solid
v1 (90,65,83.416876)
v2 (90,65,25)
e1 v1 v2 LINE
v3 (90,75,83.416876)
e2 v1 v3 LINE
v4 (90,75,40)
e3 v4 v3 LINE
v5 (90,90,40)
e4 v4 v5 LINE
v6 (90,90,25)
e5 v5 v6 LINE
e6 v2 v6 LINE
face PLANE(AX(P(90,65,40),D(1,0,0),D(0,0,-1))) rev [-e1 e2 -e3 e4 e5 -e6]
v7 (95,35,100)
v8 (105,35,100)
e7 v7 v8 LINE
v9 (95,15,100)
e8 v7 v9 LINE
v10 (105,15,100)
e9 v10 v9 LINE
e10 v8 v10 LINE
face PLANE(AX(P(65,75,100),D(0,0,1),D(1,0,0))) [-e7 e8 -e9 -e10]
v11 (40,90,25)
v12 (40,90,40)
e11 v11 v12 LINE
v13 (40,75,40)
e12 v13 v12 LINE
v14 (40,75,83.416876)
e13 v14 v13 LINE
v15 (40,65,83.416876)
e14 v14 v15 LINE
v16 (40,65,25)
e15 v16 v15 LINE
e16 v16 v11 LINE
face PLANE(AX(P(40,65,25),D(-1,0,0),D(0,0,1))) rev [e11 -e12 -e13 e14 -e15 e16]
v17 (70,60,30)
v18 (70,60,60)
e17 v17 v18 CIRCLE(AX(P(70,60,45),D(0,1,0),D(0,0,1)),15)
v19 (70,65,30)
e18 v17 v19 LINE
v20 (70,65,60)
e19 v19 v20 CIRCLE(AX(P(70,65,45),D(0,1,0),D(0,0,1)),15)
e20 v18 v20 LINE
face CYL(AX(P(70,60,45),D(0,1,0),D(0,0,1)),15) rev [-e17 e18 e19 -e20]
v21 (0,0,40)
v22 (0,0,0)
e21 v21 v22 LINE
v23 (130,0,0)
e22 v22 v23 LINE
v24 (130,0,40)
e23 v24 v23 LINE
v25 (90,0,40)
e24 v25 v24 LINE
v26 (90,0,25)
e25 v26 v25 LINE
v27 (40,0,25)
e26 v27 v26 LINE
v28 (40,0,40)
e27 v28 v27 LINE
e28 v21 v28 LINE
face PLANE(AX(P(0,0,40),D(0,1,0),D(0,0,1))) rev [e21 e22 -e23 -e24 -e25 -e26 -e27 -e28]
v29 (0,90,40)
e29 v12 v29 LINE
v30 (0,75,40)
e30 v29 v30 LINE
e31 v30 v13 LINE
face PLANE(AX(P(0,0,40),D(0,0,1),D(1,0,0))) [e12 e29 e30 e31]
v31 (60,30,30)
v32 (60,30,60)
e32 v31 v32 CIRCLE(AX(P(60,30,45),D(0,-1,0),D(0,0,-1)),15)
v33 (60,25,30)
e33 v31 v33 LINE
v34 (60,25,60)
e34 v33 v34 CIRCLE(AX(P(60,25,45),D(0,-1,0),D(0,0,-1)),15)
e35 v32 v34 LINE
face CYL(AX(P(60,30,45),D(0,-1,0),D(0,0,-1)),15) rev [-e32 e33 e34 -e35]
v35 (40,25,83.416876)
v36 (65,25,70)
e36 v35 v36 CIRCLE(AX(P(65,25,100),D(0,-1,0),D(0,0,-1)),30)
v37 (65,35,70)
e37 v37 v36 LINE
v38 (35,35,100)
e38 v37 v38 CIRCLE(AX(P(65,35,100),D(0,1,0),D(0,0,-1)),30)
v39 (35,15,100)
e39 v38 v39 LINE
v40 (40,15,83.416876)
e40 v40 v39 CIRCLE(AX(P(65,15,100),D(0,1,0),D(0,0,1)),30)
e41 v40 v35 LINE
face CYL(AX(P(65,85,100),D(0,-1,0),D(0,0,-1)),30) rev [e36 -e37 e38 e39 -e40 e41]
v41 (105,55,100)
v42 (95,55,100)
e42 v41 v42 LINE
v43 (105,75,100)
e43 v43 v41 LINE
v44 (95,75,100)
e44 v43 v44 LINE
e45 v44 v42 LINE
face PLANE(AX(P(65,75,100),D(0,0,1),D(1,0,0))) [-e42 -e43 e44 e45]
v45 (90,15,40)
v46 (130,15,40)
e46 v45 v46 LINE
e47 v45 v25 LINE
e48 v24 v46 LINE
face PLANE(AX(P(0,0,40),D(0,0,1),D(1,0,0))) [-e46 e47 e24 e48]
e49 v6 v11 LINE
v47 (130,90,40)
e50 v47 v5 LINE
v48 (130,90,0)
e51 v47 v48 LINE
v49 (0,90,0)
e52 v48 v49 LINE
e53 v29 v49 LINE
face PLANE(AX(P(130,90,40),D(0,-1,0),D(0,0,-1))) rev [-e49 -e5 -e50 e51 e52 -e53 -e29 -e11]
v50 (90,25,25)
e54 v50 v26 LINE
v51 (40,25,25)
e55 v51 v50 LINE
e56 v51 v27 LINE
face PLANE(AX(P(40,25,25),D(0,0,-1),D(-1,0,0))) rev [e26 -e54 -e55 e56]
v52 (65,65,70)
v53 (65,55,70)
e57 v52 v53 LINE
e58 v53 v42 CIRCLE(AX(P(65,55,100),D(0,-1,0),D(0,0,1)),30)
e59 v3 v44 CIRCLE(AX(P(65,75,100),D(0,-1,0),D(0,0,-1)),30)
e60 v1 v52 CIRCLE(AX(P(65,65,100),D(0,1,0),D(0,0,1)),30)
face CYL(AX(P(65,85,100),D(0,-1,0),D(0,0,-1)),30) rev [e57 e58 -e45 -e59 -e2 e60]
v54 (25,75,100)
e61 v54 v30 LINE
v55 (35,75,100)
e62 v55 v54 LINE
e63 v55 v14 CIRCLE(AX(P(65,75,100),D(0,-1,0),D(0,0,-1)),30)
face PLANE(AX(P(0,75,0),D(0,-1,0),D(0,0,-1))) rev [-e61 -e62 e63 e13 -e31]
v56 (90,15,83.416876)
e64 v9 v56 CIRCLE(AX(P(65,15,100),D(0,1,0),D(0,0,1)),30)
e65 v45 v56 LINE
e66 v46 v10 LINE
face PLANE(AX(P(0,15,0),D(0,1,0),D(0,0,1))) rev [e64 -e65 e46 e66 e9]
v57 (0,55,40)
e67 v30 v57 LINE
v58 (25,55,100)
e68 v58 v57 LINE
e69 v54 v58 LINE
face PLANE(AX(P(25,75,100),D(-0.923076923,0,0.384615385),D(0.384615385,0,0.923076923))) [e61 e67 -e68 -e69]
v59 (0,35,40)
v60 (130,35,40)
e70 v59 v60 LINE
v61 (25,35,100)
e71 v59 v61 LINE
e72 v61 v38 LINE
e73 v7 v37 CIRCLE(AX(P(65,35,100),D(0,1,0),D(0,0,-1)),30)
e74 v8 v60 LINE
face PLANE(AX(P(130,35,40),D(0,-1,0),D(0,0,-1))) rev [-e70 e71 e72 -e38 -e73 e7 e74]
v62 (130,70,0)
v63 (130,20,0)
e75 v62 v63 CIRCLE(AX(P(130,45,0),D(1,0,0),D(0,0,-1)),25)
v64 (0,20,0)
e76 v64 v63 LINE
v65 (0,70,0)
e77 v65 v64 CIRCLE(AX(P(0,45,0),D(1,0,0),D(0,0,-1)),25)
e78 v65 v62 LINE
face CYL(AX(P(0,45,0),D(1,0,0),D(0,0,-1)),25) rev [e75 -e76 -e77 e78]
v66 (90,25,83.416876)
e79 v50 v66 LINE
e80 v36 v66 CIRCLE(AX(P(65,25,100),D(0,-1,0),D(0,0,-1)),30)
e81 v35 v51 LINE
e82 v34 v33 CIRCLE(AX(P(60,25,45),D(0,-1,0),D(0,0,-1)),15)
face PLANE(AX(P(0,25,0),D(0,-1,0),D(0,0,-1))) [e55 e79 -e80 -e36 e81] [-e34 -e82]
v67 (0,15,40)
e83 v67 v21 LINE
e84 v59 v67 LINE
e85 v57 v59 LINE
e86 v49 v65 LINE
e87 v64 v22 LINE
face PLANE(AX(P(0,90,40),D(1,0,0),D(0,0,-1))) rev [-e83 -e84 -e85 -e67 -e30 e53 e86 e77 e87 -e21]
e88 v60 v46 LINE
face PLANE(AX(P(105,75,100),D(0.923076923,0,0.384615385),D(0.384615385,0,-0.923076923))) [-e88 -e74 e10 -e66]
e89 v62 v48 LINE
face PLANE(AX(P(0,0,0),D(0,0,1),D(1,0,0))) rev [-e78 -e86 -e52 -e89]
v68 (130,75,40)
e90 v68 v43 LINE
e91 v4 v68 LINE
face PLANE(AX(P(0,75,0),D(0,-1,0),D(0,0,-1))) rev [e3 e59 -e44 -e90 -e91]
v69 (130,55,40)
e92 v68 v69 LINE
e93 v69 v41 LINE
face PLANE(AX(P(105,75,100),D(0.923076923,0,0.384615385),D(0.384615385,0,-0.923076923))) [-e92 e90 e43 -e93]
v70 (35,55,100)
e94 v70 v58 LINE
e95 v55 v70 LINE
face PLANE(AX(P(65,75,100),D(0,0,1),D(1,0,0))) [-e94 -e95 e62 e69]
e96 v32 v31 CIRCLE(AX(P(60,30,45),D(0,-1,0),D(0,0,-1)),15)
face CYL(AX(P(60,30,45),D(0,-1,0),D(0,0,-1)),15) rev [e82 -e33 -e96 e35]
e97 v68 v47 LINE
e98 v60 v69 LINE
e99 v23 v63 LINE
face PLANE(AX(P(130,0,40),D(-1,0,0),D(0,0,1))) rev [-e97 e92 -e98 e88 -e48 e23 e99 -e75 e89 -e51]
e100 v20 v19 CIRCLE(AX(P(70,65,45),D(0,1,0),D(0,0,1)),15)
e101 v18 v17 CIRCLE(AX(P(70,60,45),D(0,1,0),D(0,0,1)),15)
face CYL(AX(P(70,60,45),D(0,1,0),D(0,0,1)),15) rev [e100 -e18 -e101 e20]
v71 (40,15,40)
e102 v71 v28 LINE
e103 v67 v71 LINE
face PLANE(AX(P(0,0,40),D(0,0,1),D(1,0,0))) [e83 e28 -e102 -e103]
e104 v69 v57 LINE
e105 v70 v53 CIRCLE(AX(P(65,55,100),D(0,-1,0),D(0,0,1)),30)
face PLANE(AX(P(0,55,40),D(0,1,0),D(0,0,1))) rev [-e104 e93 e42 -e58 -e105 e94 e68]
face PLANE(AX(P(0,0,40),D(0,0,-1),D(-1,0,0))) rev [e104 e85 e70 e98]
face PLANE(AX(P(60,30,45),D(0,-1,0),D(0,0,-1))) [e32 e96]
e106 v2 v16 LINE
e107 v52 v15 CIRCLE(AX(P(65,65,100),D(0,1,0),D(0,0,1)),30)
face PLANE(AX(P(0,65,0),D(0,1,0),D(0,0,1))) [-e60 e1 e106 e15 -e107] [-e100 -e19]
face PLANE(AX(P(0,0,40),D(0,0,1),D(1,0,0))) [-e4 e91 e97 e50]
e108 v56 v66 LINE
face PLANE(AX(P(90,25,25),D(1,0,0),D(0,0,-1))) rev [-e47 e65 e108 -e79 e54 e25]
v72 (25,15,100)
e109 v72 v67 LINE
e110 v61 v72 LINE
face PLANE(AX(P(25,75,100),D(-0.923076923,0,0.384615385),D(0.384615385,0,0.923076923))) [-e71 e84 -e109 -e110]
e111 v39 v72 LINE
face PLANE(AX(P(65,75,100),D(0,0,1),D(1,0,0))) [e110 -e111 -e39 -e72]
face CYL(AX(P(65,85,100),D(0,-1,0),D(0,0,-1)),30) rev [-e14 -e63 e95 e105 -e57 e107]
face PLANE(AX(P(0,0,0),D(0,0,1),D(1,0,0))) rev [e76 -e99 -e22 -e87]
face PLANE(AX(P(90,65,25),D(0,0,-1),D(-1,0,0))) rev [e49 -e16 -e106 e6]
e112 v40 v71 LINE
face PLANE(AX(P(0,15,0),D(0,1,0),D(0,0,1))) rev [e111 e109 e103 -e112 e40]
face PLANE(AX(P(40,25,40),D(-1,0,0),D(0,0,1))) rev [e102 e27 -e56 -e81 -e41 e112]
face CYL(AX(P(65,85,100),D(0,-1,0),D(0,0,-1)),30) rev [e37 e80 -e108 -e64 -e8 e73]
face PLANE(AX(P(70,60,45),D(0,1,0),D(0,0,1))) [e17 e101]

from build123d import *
from build123d.topology import SkipClean

# Parameters (mm, degrees)
BASE_BLOCK_SKETCH_W             = 130
BASE_BLOCK_SKETCH_H             = 90
BASE_BLOCK_40_DEPTH             = 40
SIDE_POCKET_A_25_DEPTH          = 25
SIDE_POCKET_B_25_DEPTH          = 25
UPPER_BOSS_50_DEPTH             = 50
WEB_BOSS_10_DEPTH               = 10
WEB_NOTCH_A_10_DEPTH            = 10
WEB_NOTCH_B_10_DEPTH            = 10
SLOT_CUT_A_60_DEPTH             = 60
SLOT_START                      = -60
SLOT_CUT_B_60_DEPTH             = 60
SLOT_CUT_C_60_DEPTH             = 60
SPOT_FACE_A_SKETCH_R            = 15
SPOT_FACE_A_30X5_DEPTH          = 5
SPOT_FACE_B_SKETCH_R            = 15
SPOT_FACE_B_30X5_DEPTH          = 5
BEARING_CRADLE_50_THROUGH_DEPTH = 130


with BuildPart() as part:
    # Base Block Sketch → Base Block 40 (new body)
    with BuildSketch(Plane.XY):
        with Locations((65, 45)):
            Rectangle(BASE_BLOCK_SKETCH_W, BASE_BLOCK_SKETCH_H)
    extrude(amount=BASE_BLOCK_40_DEPTH)

    # Side Pocket A Sketch → Side Pocket A 25 (cut)
    with BuildSketch(Plane.XZ):
        Polygon((65, 40), (40, 40), (40, 25), (90, 25), (90, 40), align=None)
    extrude(amount=-SIDE_POCKET_A_25_DEPTH, mode=Mode.SUBTRACT)

    # Side Pocket B Sketch → Side Pocket B 25 (cut)
    with BuildSketch(Plane(origin=(0, 90, 0), x_dir=(1, 0, 0), z_dir=(0, 1, 0))):
        Polygon((65, -40), (90, -40), (90, -25), (40, -25), (40, -40), align=None)
    extrude(amount=-SIDE_POCKET_B_25_DEPTH, mode=Mode.SUBTRACT)

    # Upper Boss Sketch → Upper Boss 50 (add)
    with BuildSketch(Plane.XZ.offset(-25)):
        Polygon((65, 100), (105, 100), (130, 40), (0, 40), (25, 100), align=None)
    extrude(amount=-UPPER_BOSS_50_DEPTH)

    # Web Boss Sketch → Web Boss 10 (add)
    with BuildSketch(Plane.XZ.offset(-25)):
        Polygon((0, 40), (25, 100), (105, 100), (130, 40), (90, 40), (40, 40), align=None)
    extrude(amount=WEB_BOSS_10_DEPTH)

    # Web Notch A Sketch → Web Notch A 10 (cut)
    with BuildSketch(Plane.XZ.offset(-15)):
        with BuildLine():
            Line((90, 100), (40, 100))
            ThreePointArc((40, 100), (65, 75), (90, 100))
        make_face()
        with BuildLine():
            ThreePointArc((40, 100), (65, 75), (90, 100))
            Line((90, 100), (90, 40))
            Line((90, 40), (40, 40))
            Line((40, 40), (40, 100))
        make_face()
    extrude(amount=-WEB_NOTCH_A_10_DEPTH, mode=Mode.SUBTRACT)

    # Web Notch B Sketch → Web Notch B 10 (cut)
    with BuildSketch(Plane(origin=(0, 75, 0), x_dir=(1, 0, 0), z_dir=(0, 1, 0))):
        with BuildLine():
            ThreePointArc((90, -100), (65, -75), (40, -100))
            Line((40, -100), (40, -40))
            Line((40, -40), (90, -40))
            Line((90, -40), (90, -100))
        make_face()
        with BuildLine():
            ThreePointArc((90, -100), (65, -75), (40, -100))
            Line((40, -100), (90, -100))
        make_face()
    extrude(amount=-WEB_NOTCH_B_10_DEPTH, mode=Mode.SUBTRACT)

    # Slot Cut A Sketch → Slot Cut A 60 (cut)
    with BuildSketch(Plane.XZ.offset(-25)):
        with BuildLine():
            Line((35, 100), (95, 100))
            ThreePointArc((95, 100), (65, 70), (35, 100))
        make_face()
    extrude(amount=-SLOT_CUT_A_60_DEPTH, mode=Mode.SUBTRACT)

    # Slot Cut B Sketch → Slot Cut B 60 (cut)
    with SkipClean():  # the faces are left unmerged after this step: merging them gives an invalid solid
        with BuildSketch(Plane(origin=(0, 25, 0), x_dir=(1, 0, 0), z_dir=(0, 1, 0)).offset(SLOT_START)):
            with BuildLine():
                Line((40, -100), (40, -83.416876048))
                ThreePointArc((40, -83.416876048), (36.277186767, -91.339745962), (35, -100))
                Line((35, -100), (40, -100))
            make_face()
            with BuildLine():
                Line((90, -100), (90, -83.416876048))
                ThreePointArc((90, -83.416876048), (93.722813233, -91.339745962), (95, -100))
                Line((95, -100), (90, -100))
            make_face()
        extrude(amount=SLOT_CUT_B_60_DEPTH, mode=Mode.SUBTRACT)

    # Slot Cut C Sketch → Slot Cut C 60 (cut)
    with SkipClean():  # the faces are left unmerged after this step: merging them gives an invalid solid
        with BuildSketch(Plane.XY.offset(100)):
            Polygon((25, 55), (105, 55), (130, 55), (130, 35), (0, 35), (0, 55), align=None)
        extrude(amount=-SLOT_CUT_C_60_DEPTH, mode=Mode.SUBTRACT)

    # Spot Face A Sketch → Spot Face A Ø30x5 (cut)
    with SkipClean():  # the faces are left unmerged after this step: merging them gives an invalid solid
        with BuildSketch(Plane.XZ.offset(-25)):
            with Locations(Location((60, 45, 0), (0, 0, 270))):
                Circle(SPOT_FACE_A_SKETCH_R)
        extrude(amount=-SPOT_FACE_A_30X5_DEPTH, mode=Mode.SUBTRACT)

    # Spot Face B Sketch → Spot Face B Ø30x5 (cut)
    with SkipClean():  # the faces are left unmerged after this step: merging them gives an invalid solid
        with BuildSketch(Plane(origin=(0, 65, 0), x_dir=(1, 0, 0), z_dir=(0, 1, 0))):
            with Locations(Location((70, -45, 0), (0, 0, 270))):
                Circle(SPOT_FACE_B_SKETCH_R)
        extrude(amount=-SPOT_FACE_B_30X5_DEPTH, mode=Mode.SUBTRACT)

    # Bearing Cradle Sketch → Bearing Cradle Ø50 Through (cut)
    with SkipClean():  # the faces are left unmerged after this step: merging them gives an invalid solid
        with BuildSketch(Plane(origin=(130, 0, 0), x_dir=(0, 0, -1), z_dir=(1, 0, 0))):
            with BuildLine():
                Line((0, 70), (0, 20))
                ThreePointArc((0, 20), (-25, 45), (0, 70))
            make_face()
        extrude(amount=-BEARING_CRADLE_50_THROUGH_DEPTH, mode=Mode.SUBTRACT)


solid = part.part
